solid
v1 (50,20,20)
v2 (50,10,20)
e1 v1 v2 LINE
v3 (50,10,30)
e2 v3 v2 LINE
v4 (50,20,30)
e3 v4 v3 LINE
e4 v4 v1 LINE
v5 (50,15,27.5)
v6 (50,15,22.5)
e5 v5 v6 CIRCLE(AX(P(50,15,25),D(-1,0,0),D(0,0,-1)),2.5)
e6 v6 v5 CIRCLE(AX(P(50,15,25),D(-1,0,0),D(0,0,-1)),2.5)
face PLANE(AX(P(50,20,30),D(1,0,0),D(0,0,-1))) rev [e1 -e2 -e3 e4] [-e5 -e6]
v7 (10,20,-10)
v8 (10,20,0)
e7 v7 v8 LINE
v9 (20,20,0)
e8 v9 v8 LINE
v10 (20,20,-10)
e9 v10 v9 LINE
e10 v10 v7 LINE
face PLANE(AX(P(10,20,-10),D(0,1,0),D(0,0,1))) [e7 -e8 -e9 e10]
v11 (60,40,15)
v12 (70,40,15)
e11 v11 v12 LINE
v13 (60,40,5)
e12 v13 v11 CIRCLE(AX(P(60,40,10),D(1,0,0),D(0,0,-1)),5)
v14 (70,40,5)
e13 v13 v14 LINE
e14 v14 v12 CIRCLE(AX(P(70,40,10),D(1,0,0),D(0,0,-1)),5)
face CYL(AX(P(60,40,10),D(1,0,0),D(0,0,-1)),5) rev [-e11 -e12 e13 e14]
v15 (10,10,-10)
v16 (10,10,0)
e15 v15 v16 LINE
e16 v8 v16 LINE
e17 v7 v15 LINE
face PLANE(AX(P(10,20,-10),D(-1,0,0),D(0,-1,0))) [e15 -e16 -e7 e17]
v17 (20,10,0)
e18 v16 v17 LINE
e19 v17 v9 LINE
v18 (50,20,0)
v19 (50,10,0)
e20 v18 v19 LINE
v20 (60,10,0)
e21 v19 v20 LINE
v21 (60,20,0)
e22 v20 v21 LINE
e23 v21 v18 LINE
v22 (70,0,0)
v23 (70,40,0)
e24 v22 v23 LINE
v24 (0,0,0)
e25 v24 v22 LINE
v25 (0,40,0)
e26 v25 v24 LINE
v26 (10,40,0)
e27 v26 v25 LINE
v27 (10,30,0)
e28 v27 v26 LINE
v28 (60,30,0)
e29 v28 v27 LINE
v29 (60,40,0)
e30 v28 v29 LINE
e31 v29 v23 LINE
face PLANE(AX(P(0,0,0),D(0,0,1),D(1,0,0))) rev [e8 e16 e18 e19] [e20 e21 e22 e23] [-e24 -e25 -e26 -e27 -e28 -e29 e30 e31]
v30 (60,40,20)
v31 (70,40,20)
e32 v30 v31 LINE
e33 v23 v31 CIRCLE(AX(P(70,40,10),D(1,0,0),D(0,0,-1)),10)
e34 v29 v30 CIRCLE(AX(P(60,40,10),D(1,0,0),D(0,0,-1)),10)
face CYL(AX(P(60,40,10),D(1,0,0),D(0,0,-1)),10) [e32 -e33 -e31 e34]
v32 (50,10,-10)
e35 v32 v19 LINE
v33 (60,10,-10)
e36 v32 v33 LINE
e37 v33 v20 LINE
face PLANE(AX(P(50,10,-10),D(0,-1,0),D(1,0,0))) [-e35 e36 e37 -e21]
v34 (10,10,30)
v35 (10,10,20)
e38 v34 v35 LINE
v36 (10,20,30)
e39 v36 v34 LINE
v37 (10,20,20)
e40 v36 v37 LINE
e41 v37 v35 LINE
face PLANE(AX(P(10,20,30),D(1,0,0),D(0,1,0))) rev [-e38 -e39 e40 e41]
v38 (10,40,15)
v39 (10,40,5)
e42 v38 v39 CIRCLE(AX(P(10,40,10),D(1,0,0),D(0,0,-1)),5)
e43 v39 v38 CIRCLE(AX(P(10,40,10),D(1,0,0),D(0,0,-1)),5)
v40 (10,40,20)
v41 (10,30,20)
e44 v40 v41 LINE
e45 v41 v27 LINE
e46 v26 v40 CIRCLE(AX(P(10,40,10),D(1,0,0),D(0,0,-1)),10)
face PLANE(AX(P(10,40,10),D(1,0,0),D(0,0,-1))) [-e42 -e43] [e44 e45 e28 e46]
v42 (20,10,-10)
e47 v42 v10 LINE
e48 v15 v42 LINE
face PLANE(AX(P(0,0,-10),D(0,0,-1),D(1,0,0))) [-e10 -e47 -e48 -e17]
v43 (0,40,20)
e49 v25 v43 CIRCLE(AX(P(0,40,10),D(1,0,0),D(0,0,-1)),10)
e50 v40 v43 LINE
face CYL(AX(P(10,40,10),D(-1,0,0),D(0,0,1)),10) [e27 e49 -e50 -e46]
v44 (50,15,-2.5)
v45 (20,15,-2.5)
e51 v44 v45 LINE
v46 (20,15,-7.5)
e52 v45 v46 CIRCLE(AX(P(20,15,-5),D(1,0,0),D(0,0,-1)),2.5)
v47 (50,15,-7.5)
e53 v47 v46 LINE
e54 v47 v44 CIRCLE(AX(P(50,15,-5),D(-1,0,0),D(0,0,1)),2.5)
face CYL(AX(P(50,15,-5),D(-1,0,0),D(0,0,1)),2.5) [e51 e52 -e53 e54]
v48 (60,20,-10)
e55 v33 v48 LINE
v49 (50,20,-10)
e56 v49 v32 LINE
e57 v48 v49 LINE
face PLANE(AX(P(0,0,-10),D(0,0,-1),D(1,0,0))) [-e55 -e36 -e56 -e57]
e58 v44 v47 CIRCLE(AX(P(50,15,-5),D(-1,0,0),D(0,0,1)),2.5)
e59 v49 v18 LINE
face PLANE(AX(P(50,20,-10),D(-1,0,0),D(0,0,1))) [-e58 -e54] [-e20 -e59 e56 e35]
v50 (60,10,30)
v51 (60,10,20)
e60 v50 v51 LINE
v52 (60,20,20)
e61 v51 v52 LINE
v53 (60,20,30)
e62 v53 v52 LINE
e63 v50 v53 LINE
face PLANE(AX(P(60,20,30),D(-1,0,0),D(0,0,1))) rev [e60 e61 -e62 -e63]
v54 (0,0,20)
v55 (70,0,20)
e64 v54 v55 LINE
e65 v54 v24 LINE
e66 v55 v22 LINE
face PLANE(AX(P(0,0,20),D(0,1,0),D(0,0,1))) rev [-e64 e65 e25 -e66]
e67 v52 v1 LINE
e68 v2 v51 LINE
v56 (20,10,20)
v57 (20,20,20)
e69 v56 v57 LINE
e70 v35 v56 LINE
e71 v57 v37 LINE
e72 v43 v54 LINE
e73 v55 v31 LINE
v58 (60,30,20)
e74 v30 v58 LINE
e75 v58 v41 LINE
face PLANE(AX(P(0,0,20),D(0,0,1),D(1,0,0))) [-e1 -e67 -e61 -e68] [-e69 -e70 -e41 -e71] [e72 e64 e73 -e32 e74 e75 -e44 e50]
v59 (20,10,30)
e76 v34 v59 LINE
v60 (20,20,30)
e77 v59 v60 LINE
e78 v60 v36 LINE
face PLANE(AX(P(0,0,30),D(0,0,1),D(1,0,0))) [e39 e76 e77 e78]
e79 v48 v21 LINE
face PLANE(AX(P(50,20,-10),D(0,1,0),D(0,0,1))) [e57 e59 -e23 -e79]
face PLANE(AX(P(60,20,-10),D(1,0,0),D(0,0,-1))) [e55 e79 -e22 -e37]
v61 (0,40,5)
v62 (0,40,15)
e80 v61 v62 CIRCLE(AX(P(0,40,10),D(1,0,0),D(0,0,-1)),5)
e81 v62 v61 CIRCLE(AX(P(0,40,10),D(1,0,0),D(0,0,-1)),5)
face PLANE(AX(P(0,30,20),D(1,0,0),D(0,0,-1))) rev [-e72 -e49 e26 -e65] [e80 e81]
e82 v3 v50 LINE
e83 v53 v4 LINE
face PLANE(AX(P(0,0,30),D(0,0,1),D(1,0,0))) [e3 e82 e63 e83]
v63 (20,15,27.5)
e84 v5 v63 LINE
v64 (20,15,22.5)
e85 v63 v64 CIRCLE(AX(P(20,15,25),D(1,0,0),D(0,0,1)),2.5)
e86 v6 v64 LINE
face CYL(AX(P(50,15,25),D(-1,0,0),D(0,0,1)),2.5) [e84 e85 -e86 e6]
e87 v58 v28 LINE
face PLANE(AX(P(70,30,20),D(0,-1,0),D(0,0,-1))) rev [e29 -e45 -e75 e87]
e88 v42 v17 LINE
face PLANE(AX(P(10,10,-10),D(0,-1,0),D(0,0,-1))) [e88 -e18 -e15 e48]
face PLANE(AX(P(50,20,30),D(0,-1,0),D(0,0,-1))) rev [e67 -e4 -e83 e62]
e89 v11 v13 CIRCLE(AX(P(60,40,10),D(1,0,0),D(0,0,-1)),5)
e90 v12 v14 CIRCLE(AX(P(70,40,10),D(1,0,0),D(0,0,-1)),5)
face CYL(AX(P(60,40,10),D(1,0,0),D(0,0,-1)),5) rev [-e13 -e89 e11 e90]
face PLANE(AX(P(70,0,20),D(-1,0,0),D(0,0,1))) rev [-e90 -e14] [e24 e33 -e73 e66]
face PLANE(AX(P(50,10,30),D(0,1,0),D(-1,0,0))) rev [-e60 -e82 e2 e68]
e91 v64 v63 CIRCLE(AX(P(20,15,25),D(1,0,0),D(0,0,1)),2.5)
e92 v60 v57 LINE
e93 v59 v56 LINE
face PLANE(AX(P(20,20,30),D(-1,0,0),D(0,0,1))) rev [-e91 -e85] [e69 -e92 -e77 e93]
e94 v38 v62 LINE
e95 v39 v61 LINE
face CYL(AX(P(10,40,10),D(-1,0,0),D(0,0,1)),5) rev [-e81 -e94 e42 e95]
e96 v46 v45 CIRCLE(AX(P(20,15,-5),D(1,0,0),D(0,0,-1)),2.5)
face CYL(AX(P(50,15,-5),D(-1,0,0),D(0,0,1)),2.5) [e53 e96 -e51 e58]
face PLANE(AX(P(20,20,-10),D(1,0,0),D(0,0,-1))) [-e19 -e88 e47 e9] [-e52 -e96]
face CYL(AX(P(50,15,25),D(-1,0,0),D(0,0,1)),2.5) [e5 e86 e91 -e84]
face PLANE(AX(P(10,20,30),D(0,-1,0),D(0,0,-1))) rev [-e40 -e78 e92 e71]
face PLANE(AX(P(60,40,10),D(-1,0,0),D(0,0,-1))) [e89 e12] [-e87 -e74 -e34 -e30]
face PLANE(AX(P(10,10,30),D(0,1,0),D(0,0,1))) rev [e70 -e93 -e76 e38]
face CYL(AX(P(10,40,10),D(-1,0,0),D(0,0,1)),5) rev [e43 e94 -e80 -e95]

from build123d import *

# Parameters (mm, degrees)
BASE_BLOCK_SKETCH_W   = 70
BASE_BLOCK_SKETCH_H   = 30
BASE_BLOCK_DEPTH      = 20
HINGE_EAR_SKETCH_R    = 5
HINGE_EAR_DEPTH       = 10
SIDE_BLOCK_SKETCH_W   = 10
SIDE_BLOCK_SKETCH_H   = 10
SIDE_BLOCK_DEPTH      = 10
STOP_BLOCK_SKETCH_W   = 10
STOP_BLOCK_SKETCH_H   = 10
STOP_BLOCK_10MM_DEPTH = 10
ROD_SKETCH_R          = 2.5
ROD_30MM_DEPTH        = 30


with BuildPart() as part:
    # Base Block Sketch → Base Block (new body)
    with BuildSketch(Plane.XY):
        with Locations((35, 15)):
            Rectangle(BASE_BLOCK_SKETCH_W, BASE_BLOCK_SKETCH_H)
    extrude(amount=BASE_BLOCK_DEPTH)

    # Hinge Ear Sketch → Hinge Ear (add)
    with BuildSketch(Plane(origin=(0, 0, 0), x_dir=(0, 0, -1), z_dir=(1, 0, 0))):
        with BuildLine():
            Line((-20, 40), (-20, 30))
            Line((-20, 30), (0, 30))
            Line((0, 30), (0, 40))
            ThreePointArc((0, 40), (-10, 50), (-20, 40))
        make_face()
        with Locations((-10, 40)):
            Circle(HINGE_EAR_SKETCH_R, mode=Mode.SUBTRACT)
    hinge_ear = extrude(amount=HINGE_EAR_DEPTH)

    # Hinge Ear Mirror: Hinge Ear across plane
    add(hinge_ear.mirror(Plane(origin=(35, 0, 0), x_dir=(0, 0, 1), z_dir=(1, 0, 0))))

    # Side Block Sketch → Side Block (add)
    with BuildSketch(Plane.XY.offset(20)):
        with Locations((55, 15)):
            Rectangle(SIDE_BLOCK_SKETCH_W, SIDE_BLOCK_SKETCH_H)
    side_block = extrude(amount=SIDE_BLOCK_DEPTH)

    # Stop Block Sketch → Stop Block 10mm (add)
    with BuildSketch(Plane.XY.offset(20)):
        with Locations((15, 15)):
            Rectangle(STOP_BLOCK_SKETCH_W, STOP_BLOCK_SKETCH_H)
    stop_block_10mm = extrude(amount=STOP_BLOCK_10MM_DEPTH)

    # Rod Sketch → Rod 30mm (add)
    with BuildSketch(Plane(origin=(20, 0, 0), x_dir=(0, 0, -1), z_dir=(1, 0, 0))):
        with Locations(Location((-25, 15, 0), (0, 0, 180))):
            Circle(ROD_SKETCH_R)
    rod_30mm = extrude(amount=ROD_30MM_DEPTH)

    # Block and Rod Mirror: Side Block, Stop Block 10mm, Rod 30mm across plane
    add(side_block.mirror(Plane.XY.offset(10)))
    add(stop_block_10mm.mirror(Plane.XY.offset(10)))
    add(rod_30mm.mirror(Plane.XY.offset(10)))


solid = part.part
